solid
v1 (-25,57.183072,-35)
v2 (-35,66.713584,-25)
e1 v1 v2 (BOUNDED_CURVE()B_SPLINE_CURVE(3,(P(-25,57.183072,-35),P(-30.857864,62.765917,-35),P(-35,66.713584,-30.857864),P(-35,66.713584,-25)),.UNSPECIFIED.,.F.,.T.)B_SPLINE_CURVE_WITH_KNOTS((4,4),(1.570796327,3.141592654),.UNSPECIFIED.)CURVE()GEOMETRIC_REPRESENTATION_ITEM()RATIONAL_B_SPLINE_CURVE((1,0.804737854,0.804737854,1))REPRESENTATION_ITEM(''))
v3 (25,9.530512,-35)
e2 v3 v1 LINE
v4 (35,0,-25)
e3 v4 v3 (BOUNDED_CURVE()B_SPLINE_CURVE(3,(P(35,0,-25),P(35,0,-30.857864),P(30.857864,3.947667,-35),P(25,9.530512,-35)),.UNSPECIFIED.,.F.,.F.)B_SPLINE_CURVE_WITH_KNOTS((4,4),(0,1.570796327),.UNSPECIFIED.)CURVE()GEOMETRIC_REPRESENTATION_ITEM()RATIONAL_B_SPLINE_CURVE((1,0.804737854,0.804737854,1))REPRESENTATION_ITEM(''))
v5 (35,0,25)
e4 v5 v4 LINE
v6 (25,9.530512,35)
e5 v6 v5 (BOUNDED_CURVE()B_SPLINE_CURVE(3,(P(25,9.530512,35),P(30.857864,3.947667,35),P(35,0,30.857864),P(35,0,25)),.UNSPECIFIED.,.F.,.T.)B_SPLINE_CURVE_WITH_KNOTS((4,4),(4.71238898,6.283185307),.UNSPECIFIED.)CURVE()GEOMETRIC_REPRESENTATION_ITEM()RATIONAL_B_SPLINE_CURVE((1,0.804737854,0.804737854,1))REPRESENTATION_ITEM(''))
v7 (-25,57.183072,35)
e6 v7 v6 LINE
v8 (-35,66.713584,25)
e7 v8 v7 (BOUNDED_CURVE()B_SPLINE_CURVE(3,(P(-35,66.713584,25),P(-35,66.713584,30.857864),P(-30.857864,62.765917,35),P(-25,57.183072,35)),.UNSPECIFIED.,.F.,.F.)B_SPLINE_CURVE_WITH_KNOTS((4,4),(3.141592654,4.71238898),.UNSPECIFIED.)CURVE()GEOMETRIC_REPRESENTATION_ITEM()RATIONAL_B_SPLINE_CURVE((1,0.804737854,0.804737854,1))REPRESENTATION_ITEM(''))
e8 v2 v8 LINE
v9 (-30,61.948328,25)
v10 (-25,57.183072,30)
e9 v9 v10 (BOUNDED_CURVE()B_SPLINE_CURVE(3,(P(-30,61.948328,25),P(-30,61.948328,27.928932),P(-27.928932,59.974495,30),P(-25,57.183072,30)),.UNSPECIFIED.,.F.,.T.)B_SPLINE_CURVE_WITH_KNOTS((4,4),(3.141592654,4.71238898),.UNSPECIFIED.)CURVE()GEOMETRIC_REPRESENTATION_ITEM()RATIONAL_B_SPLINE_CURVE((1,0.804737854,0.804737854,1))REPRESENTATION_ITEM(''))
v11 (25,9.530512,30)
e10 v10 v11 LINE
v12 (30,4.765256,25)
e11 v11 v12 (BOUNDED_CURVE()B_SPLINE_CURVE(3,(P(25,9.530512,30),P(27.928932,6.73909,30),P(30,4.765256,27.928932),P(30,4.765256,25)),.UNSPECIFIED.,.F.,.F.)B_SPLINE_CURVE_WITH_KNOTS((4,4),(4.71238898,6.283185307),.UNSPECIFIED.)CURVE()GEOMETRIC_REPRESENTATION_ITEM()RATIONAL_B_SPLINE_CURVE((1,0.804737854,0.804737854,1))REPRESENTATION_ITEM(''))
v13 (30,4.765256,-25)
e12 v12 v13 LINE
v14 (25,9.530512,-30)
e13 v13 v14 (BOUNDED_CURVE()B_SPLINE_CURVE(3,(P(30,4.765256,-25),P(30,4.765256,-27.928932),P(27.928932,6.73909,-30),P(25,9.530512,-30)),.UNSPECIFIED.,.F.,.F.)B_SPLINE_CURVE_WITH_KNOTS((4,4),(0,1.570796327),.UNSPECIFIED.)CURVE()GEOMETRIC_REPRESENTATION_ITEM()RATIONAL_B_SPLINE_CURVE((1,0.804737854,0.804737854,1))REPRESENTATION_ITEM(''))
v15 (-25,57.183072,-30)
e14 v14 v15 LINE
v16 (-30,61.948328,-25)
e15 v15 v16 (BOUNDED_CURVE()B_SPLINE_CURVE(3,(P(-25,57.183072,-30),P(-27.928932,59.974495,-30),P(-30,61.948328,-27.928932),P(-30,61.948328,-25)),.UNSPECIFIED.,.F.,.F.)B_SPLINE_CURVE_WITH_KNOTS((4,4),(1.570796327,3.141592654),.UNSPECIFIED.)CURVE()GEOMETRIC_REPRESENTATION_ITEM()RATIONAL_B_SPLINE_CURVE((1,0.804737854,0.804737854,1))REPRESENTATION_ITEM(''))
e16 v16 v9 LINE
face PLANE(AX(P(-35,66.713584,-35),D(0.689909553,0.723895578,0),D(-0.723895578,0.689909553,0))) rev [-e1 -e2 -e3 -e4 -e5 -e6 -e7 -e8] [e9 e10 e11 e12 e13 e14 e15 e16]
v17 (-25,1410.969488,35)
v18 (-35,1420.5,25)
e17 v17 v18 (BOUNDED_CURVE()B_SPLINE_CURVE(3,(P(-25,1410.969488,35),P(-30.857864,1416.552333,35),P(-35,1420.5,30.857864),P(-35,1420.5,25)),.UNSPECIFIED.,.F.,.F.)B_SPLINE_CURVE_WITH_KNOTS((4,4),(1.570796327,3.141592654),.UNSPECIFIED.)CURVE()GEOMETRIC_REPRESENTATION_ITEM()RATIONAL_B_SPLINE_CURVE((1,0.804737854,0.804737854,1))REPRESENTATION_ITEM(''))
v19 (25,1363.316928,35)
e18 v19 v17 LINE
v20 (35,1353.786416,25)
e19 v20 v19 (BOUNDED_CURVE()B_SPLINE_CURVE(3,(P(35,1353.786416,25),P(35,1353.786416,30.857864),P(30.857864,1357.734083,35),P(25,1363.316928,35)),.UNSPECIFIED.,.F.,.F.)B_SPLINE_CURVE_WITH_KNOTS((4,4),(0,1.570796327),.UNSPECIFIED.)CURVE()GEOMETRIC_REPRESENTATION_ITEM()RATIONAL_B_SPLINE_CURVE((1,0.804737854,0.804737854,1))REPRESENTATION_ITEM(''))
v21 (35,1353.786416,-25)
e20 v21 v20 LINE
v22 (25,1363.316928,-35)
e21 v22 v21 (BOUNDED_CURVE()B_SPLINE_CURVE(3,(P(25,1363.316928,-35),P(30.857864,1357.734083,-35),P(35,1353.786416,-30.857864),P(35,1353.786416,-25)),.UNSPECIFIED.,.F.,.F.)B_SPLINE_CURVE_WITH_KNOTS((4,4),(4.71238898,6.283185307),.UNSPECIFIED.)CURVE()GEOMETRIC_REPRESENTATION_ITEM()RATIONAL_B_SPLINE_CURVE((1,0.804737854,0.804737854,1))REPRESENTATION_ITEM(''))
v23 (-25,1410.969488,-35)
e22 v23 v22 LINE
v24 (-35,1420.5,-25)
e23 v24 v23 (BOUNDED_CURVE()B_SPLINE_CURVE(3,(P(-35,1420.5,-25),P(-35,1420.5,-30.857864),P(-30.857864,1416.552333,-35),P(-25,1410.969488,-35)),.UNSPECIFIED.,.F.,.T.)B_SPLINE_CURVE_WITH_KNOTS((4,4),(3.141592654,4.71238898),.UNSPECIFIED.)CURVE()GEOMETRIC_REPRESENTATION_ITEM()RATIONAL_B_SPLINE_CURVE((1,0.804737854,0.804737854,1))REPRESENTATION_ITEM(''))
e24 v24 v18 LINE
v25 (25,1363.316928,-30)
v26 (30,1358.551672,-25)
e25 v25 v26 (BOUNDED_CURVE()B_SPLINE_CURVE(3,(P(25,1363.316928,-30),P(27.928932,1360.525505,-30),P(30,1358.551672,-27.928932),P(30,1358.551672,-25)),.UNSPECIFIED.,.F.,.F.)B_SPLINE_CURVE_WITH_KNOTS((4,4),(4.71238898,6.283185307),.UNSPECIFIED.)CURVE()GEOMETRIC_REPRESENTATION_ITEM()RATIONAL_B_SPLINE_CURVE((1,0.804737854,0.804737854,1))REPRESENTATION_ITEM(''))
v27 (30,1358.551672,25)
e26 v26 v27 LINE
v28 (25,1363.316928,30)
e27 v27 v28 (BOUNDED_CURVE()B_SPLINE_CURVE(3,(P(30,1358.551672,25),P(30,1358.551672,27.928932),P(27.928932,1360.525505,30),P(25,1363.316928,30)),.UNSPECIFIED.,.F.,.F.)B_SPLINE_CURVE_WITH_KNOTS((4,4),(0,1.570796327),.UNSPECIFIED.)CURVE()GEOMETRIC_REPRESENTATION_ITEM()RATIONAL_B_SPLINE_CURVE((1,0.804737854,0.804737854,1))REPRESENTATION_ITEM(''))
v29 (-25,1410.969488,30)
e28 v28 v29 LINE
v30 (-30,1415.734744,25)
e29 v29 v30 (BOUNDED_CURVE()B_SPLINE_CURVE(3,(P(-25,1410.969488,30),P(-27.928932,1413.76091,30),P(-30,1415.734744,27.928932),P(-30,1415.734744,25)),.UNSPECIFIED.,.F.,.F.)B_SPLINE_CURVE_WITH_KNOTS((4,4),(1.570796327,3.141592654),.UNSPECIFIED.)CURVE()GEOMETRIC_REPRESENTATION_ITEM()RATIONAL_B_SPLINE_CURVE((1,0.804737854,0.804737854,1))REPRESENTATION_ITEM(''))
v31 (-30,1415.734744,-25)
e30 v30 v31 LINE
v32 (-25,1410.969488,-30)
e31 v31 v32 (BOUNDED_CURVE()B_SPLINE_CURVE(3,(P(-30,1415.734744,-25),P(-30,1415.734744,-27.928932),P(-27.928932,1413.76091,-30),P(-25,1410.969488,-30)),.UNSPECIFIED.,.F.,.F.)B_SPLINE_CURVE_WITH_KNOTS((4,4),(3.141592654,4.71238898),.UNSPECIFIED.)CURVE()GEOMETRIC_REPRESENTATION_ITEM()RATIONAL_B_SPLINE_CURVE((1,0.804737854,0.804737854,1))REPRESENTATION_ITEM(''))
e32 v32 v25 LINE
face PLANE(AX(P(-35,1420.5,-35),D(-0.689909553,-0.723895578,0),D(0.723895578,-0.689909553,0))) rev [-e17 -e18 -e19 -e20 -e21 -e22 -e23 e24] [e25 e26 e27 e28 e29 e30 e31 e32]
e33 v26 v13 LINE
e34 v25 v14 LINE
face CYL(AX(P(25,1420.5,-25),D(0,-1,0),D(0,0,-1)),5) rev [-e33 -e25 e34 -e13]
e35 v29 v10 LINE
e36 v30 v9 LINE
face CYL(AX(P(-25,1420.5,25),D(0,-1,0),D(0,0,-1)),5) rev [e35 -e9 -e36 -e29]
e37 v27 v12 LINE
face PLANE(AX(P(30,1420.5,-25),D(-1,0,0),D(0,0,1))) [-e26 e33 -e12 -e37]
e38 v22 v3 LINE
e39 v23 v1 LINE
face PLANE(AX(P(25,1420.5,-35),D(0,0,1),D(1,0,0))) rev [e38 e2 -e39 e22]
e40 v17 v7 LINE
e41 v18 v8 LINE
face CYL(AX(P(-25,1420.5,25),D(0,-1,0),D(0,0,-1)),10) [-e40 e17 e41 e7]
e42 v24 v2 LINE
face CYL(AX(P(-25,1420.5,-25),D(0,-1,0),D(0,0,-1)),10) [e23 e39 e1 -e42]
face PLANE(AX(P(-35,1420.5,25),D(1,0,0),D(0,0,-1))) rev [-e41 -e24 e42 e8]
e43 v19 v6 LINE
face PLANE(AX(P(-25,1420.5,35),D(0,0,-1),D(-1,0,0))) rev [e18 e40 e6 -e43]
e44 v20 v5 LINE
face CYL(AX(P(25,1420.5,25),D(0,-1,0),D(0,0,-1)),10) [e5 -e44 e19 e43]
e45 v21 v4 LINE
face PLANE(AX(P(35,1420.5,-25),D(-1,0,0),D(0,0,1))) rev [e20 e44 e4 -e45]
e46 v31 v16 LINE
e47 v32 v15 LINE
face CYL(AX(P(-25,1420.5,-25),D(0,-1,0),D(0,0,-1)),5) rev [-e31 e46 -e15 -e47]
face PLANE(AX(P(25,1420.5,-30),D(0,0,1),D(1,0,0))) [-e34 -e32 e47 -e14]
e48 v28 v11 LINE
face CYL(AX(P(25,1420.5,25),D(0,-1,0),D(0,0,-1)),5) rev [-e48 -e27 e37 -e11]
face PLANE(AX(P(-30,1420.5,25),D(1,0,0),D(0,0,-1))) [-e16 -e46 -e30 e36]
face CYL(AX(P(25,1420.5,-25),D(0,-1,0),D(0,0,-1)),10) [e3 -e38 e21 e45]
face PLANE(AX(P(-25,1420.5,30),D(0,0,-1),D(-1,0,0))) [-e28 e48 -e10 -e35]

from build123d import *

# Parameters (mm, degrees)
FEATURE_19_WELDMEMBERFEAT_4_MORE_IN_5_DEPTH = 1420.5
CUT_EXTRUDE1_DEPTH                          = 1423.654297431
CUT_EXTRUDE1_DEPTH_BACK                     = 1423.654297431


with BuildPart() as part:
    # Sketch1 → feature 19 (WeldMemberFeat) (+4 more in 5 files) Cold-formed Hollow Structural Square Steel(gb t6728-2002) 70×70×5(1) (new body)
    with BuildSketch(Plane(origin=(0, 0, 0), x_dir=(-1, 0, 0), z_dir=(0, 1, 0))):
        with BuildLine():
            Line((-25, -35), (25, -35))
            ThreePointArc((25, -35), (32.071067812, -32.071067812), (35, -25))
            Line((35, -25), (35, 25))
            ThreePointArc((35, 25), (32.071067812, 32.071067812), (25, 35))
            Line((25, 35), (-25, 35))
            ThreePointArc((-25, 35), (-32.071067812, 32.071067812), (-35, 25))
            Line((-35, 25), (-35, -25))
            ThreePointArc((-35, -25), (-32.071067812, -32.071067812), (-25, -35))
        make_face()
        with BuildLine():
            Line((-25, -30), (25, -30))
            ThreePointArc((25, -30), (28.535533906, -28.535533906), (30, -25))
            Line((30, -25), (30, 25))
            ThreePointArc((30, 25), (28.535533906, 28.535533906), (25, 30))
            Line((25, 30), (-25, 30))
            ThreePointArc((-25, 30), (-28.535533906, 28.535533906), (-30, 25))
            Line((-30, 25), (-30, -25))
            ThreePointArc((-30, -25), (-28.535533906, -28.535533906), (-25, -30))
        make_face(mode=Mode.SUBTRACT)
    extrude(amount=FEATURE_19_WELDMEMBERFEAT_4_MORE_IN_5_DEPTH)

    # 0:feat:20/0 feature 20/0 (ProfileFeature) (+11 more in 7 files) Sketch2 → Cut-Extrude1 (cut, two sides: drawn at the far end of the back side and taken through both)
    with BuildSketch(Plane.XY.offset(35).offset(-CUT_EXTRUDE1_DEPTH_BACK)):
        Polygon((-35, 66.713584391), (35, 0), (-35, 0), align=None)
        Polygon((-35, 1420.5), (35, 1353.786415609), (35, 1420.5), align=None)
    extrude(amount=CUT_EXTRUDE1_DEPTH + CUT_EXTRUDE1_DEPTH_BACK, mode=Mode.SUBTRACT)


solid = part.part
